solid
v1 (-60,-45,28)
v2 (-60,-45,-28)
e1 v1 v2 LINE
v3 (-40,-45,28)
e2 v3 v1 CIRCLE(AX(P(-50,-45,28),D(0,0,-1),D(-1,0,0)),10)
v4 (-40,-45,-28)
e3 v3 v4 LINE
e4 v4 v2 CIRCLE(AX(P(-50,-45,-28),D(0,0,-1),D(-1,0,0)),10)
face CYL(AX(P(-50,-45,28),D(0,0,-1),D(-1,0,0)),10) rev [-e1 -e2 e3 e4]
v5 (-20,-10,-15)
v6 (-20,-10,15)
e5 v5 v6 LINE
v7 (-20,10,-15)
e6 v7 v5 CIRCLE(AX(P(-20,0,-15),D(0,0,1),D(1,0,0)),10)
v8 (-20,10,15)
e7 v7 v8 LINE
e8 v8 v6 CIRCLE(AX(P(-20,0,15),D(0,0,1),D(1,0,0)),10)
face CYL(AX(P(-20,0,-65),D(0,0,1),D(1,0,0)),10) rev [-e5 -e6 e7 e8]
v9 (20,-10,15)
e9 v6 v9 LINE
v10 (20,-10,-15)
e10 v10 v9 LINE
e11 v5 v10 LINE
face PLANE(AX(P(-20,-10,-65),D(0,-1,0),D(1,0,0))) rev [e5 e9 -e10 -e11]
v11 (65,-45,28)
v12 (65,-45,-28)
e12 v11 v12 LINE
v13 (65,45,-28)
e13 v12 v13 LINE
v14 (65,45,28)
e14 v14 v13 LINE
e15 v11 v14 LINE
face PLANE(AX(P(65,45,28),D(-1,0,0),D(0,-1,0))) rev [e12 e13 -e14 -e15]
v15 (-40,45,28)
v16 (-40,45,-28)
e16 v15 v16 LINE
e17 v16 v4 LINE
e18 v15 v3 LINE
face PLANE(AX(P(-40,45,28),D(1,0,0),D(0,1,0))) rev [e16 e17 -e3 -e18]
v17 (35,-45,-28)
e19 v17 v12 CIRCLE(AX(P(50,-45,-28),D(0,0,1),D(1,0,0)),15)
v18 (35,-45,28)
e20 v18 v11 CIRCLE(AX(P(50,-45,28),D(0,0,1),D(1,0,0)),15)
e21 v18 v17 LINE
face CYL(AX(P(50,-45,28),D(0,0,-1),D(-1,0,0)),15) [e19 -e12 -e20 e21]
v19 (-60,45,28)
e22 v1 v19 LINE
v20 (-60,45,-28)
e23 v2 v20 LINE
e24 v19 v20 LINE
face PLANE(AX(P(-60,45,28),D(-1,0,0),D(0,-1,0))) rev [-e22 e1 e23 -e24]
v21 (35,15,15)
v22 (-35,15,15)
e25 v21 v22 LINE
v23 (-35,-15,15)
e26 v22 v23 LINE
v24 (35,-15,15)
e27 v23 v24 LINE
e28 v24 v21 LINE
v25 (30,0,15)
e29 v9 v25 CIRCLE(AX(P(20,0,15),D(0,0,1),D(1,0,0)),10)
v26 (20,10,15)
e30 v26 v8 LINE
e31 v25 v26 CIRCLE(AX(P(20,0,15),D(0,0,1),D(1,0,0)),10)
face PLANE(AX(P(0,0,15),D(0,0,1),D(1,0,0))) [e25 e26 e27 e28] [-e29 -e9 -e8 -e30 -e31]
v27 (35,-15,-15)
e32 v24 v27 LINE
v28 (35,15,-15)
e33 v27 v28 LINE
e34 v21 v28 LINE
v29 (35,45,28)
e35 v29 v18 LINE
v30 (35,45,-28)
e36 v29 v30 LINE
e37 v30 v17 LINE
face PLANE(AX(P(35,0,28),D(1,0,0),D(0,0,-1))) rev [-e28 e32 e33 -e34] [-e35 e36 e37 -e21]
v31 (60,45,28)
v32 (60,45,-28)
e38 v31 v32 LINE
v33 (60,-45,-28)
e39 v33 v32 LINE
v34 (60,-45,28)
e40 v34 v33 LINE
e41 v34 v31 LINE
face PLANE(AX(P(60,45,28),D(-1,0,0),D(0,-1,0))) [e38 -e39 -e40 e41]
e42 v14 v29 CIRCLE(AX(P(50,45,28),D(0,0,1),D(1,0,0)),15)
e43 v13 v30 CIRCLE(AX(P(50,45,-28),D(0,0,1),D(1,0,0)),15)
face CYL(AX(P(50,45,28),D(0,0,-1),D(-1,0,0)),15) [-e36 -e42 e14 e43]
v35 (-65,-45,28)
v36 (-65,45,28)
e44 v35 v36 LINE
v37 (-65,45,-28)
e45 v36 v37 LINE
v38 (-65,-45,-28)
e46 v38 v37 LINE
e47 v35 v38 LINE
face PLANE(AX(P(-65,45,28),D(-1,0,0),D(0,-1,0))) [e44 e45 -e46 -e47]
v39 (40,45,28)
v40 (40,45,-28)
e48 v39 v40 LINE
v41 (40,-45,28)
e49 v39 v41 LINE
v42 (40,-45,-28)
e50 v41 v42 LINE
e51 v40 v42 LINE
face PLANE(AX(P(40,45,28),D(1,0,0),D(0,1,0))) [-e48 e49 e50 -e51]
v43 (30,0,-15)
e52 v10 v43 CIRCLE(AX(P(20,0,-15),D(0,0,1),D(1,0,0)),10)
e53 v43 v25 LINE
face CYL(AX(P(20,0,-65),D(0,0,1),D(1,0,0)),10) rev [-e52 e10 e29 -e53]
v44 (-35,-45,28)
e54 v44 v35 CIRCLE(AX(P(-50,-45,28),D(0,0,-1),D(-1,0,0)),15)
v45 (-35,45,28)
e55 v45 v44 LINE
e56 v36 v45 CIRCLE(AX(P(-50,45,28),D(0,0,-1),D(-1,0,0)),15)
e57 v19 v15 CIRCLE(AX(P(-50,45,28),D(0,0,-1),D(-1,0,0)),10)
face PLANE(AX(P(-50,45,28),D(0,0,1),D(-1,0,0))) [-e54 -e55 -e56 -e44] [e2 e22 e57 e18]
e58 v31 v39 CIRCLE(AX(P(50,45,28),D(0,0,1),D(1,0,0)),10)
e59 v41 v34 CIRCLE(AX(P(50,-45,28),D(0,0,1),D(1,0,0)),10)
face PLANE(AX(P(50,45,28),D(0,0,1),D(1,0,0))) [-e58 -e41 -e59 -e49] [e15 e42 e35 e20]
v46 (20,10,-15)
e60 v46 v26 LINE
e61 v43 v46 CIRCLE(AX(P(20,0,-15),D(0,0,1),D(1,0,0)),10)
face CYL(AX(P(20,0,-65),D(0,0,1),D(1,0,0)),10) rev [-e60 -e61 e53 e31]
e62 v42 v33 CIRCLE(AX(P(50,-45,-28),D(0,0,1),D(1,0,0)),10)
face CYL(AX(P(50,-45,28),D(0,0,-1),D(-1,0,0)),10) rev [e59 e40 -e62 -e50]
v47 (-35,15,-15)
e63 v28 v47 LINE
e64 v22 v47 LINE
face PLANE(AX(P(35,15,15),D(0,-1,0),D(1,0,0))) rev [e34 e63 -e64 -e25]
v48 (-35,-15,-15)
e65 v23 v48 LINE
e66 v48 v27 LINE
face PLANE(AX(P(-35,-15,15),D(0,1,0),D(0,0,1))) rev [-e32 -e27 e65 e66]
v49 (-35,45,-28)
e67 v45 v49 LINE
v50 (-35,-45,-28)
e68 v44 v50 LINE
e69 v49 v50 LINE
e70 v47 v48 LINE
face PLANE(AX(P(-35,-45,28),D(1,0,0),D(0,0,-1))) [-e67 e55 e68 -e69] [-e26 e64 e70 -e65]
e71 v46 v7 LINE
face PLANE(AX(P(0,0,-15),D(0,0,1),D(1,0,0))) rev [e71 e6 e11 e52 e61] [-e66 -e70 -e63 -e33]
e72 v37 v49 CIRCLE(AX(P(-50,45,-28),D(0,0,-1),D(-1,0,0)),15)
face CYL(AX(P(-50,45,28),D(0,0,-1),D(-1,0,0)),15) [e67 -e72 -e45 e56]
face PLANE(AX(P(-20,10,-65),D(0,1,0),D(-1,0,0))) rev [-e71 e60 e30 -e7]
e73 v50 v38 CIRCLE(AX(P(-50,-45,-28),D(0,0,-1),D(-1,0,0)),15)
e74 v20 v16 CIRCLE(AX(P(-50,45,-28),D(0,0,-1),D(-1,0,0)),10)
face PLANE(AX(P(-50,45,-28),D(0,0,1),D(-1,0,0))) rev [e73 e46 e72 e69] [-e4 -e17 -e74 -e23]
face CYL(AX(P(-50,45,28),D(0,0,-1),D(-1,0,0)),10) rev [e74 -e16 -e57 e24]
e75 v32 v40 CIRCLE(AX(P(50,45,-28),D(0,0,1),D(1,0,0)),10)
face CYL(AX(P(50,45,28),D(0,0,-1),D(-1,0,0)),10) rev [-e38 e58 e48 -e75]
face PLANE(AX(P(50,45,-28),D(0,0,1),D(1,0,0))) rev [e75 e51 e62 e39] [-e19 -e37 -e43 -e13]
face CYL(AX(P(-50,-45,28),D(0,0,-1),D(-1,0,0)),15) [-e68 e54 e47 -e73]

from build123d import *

# Parameters (mm, degrees)
CENTER_WEB_DEPTH     = 15
WEB_WINDOW_CUT_DEPTH = 80
SIDE_LOOP_DEPTH      = 28


with BuildPart() as part:
    # Center Web Profile → Center Web (new, symmetric)
    with BuildSketch(Plane.XY):
        Polygon((35, 0), (35, 15), (-35, 15), (-35, -15), (35, -15), align=None)
    extrude(amount=CENTER_WEB_DEPTH, both=True)

    # Web Window Profile 40x20 → Web Window Cut (cut)
    with BuildSketch(Plane.XY.offset(15)):
        with BuildLine():
            Line((-20, 10), (20, 10))
            ThreePointArc((20, 10), (30, 0), (20, -10))
            Line((20, -10), (-20, -10))
            ThreePointArc((-20, -10), (-30, 0), (-20, 10))
        make_face()
    extrude(amount=-WEB_WINDOW_CUT_DEPTH, mode=Mode.SUBTRACT)

    # Side Loop Profile → Side Loop (add, symmetric)
    with BuildSketch(Plane.XY):
        with BuildLine():
            Line((35, 0), (35, 45))
            ThreePointArc((35, 45), (50, 60), (65, 45))
            Line((65, 45), (65, -45))
            ThreePointArc((65, -45), (50, -60), (35, -45))
            Line((35, -45), (35, -15))
            Line((35, -15), (35, 0))
        make_face()
        with BuildLine():
            Line((60, 45), (60, -45))
            ThreePointArc((60, -45), (50, -55), (40, -45))
            Line((40, -45), (40, 45))
            ThreePointArc((40, 45), (50, 55), (60, 45))
        make_face(mode=Mode.SUBTRACT)
    side_loop = extrude(amount=SIDE_LOOP_DEPTH, both=True)

    # Side Loop Mirror: Side Loop across plane
    add(side_loop.mirror(Plane(origin=(0, 0, 0), x_dir=(0, 0, 1), z_dir=(1, 0, 0))))


solid = part.part
